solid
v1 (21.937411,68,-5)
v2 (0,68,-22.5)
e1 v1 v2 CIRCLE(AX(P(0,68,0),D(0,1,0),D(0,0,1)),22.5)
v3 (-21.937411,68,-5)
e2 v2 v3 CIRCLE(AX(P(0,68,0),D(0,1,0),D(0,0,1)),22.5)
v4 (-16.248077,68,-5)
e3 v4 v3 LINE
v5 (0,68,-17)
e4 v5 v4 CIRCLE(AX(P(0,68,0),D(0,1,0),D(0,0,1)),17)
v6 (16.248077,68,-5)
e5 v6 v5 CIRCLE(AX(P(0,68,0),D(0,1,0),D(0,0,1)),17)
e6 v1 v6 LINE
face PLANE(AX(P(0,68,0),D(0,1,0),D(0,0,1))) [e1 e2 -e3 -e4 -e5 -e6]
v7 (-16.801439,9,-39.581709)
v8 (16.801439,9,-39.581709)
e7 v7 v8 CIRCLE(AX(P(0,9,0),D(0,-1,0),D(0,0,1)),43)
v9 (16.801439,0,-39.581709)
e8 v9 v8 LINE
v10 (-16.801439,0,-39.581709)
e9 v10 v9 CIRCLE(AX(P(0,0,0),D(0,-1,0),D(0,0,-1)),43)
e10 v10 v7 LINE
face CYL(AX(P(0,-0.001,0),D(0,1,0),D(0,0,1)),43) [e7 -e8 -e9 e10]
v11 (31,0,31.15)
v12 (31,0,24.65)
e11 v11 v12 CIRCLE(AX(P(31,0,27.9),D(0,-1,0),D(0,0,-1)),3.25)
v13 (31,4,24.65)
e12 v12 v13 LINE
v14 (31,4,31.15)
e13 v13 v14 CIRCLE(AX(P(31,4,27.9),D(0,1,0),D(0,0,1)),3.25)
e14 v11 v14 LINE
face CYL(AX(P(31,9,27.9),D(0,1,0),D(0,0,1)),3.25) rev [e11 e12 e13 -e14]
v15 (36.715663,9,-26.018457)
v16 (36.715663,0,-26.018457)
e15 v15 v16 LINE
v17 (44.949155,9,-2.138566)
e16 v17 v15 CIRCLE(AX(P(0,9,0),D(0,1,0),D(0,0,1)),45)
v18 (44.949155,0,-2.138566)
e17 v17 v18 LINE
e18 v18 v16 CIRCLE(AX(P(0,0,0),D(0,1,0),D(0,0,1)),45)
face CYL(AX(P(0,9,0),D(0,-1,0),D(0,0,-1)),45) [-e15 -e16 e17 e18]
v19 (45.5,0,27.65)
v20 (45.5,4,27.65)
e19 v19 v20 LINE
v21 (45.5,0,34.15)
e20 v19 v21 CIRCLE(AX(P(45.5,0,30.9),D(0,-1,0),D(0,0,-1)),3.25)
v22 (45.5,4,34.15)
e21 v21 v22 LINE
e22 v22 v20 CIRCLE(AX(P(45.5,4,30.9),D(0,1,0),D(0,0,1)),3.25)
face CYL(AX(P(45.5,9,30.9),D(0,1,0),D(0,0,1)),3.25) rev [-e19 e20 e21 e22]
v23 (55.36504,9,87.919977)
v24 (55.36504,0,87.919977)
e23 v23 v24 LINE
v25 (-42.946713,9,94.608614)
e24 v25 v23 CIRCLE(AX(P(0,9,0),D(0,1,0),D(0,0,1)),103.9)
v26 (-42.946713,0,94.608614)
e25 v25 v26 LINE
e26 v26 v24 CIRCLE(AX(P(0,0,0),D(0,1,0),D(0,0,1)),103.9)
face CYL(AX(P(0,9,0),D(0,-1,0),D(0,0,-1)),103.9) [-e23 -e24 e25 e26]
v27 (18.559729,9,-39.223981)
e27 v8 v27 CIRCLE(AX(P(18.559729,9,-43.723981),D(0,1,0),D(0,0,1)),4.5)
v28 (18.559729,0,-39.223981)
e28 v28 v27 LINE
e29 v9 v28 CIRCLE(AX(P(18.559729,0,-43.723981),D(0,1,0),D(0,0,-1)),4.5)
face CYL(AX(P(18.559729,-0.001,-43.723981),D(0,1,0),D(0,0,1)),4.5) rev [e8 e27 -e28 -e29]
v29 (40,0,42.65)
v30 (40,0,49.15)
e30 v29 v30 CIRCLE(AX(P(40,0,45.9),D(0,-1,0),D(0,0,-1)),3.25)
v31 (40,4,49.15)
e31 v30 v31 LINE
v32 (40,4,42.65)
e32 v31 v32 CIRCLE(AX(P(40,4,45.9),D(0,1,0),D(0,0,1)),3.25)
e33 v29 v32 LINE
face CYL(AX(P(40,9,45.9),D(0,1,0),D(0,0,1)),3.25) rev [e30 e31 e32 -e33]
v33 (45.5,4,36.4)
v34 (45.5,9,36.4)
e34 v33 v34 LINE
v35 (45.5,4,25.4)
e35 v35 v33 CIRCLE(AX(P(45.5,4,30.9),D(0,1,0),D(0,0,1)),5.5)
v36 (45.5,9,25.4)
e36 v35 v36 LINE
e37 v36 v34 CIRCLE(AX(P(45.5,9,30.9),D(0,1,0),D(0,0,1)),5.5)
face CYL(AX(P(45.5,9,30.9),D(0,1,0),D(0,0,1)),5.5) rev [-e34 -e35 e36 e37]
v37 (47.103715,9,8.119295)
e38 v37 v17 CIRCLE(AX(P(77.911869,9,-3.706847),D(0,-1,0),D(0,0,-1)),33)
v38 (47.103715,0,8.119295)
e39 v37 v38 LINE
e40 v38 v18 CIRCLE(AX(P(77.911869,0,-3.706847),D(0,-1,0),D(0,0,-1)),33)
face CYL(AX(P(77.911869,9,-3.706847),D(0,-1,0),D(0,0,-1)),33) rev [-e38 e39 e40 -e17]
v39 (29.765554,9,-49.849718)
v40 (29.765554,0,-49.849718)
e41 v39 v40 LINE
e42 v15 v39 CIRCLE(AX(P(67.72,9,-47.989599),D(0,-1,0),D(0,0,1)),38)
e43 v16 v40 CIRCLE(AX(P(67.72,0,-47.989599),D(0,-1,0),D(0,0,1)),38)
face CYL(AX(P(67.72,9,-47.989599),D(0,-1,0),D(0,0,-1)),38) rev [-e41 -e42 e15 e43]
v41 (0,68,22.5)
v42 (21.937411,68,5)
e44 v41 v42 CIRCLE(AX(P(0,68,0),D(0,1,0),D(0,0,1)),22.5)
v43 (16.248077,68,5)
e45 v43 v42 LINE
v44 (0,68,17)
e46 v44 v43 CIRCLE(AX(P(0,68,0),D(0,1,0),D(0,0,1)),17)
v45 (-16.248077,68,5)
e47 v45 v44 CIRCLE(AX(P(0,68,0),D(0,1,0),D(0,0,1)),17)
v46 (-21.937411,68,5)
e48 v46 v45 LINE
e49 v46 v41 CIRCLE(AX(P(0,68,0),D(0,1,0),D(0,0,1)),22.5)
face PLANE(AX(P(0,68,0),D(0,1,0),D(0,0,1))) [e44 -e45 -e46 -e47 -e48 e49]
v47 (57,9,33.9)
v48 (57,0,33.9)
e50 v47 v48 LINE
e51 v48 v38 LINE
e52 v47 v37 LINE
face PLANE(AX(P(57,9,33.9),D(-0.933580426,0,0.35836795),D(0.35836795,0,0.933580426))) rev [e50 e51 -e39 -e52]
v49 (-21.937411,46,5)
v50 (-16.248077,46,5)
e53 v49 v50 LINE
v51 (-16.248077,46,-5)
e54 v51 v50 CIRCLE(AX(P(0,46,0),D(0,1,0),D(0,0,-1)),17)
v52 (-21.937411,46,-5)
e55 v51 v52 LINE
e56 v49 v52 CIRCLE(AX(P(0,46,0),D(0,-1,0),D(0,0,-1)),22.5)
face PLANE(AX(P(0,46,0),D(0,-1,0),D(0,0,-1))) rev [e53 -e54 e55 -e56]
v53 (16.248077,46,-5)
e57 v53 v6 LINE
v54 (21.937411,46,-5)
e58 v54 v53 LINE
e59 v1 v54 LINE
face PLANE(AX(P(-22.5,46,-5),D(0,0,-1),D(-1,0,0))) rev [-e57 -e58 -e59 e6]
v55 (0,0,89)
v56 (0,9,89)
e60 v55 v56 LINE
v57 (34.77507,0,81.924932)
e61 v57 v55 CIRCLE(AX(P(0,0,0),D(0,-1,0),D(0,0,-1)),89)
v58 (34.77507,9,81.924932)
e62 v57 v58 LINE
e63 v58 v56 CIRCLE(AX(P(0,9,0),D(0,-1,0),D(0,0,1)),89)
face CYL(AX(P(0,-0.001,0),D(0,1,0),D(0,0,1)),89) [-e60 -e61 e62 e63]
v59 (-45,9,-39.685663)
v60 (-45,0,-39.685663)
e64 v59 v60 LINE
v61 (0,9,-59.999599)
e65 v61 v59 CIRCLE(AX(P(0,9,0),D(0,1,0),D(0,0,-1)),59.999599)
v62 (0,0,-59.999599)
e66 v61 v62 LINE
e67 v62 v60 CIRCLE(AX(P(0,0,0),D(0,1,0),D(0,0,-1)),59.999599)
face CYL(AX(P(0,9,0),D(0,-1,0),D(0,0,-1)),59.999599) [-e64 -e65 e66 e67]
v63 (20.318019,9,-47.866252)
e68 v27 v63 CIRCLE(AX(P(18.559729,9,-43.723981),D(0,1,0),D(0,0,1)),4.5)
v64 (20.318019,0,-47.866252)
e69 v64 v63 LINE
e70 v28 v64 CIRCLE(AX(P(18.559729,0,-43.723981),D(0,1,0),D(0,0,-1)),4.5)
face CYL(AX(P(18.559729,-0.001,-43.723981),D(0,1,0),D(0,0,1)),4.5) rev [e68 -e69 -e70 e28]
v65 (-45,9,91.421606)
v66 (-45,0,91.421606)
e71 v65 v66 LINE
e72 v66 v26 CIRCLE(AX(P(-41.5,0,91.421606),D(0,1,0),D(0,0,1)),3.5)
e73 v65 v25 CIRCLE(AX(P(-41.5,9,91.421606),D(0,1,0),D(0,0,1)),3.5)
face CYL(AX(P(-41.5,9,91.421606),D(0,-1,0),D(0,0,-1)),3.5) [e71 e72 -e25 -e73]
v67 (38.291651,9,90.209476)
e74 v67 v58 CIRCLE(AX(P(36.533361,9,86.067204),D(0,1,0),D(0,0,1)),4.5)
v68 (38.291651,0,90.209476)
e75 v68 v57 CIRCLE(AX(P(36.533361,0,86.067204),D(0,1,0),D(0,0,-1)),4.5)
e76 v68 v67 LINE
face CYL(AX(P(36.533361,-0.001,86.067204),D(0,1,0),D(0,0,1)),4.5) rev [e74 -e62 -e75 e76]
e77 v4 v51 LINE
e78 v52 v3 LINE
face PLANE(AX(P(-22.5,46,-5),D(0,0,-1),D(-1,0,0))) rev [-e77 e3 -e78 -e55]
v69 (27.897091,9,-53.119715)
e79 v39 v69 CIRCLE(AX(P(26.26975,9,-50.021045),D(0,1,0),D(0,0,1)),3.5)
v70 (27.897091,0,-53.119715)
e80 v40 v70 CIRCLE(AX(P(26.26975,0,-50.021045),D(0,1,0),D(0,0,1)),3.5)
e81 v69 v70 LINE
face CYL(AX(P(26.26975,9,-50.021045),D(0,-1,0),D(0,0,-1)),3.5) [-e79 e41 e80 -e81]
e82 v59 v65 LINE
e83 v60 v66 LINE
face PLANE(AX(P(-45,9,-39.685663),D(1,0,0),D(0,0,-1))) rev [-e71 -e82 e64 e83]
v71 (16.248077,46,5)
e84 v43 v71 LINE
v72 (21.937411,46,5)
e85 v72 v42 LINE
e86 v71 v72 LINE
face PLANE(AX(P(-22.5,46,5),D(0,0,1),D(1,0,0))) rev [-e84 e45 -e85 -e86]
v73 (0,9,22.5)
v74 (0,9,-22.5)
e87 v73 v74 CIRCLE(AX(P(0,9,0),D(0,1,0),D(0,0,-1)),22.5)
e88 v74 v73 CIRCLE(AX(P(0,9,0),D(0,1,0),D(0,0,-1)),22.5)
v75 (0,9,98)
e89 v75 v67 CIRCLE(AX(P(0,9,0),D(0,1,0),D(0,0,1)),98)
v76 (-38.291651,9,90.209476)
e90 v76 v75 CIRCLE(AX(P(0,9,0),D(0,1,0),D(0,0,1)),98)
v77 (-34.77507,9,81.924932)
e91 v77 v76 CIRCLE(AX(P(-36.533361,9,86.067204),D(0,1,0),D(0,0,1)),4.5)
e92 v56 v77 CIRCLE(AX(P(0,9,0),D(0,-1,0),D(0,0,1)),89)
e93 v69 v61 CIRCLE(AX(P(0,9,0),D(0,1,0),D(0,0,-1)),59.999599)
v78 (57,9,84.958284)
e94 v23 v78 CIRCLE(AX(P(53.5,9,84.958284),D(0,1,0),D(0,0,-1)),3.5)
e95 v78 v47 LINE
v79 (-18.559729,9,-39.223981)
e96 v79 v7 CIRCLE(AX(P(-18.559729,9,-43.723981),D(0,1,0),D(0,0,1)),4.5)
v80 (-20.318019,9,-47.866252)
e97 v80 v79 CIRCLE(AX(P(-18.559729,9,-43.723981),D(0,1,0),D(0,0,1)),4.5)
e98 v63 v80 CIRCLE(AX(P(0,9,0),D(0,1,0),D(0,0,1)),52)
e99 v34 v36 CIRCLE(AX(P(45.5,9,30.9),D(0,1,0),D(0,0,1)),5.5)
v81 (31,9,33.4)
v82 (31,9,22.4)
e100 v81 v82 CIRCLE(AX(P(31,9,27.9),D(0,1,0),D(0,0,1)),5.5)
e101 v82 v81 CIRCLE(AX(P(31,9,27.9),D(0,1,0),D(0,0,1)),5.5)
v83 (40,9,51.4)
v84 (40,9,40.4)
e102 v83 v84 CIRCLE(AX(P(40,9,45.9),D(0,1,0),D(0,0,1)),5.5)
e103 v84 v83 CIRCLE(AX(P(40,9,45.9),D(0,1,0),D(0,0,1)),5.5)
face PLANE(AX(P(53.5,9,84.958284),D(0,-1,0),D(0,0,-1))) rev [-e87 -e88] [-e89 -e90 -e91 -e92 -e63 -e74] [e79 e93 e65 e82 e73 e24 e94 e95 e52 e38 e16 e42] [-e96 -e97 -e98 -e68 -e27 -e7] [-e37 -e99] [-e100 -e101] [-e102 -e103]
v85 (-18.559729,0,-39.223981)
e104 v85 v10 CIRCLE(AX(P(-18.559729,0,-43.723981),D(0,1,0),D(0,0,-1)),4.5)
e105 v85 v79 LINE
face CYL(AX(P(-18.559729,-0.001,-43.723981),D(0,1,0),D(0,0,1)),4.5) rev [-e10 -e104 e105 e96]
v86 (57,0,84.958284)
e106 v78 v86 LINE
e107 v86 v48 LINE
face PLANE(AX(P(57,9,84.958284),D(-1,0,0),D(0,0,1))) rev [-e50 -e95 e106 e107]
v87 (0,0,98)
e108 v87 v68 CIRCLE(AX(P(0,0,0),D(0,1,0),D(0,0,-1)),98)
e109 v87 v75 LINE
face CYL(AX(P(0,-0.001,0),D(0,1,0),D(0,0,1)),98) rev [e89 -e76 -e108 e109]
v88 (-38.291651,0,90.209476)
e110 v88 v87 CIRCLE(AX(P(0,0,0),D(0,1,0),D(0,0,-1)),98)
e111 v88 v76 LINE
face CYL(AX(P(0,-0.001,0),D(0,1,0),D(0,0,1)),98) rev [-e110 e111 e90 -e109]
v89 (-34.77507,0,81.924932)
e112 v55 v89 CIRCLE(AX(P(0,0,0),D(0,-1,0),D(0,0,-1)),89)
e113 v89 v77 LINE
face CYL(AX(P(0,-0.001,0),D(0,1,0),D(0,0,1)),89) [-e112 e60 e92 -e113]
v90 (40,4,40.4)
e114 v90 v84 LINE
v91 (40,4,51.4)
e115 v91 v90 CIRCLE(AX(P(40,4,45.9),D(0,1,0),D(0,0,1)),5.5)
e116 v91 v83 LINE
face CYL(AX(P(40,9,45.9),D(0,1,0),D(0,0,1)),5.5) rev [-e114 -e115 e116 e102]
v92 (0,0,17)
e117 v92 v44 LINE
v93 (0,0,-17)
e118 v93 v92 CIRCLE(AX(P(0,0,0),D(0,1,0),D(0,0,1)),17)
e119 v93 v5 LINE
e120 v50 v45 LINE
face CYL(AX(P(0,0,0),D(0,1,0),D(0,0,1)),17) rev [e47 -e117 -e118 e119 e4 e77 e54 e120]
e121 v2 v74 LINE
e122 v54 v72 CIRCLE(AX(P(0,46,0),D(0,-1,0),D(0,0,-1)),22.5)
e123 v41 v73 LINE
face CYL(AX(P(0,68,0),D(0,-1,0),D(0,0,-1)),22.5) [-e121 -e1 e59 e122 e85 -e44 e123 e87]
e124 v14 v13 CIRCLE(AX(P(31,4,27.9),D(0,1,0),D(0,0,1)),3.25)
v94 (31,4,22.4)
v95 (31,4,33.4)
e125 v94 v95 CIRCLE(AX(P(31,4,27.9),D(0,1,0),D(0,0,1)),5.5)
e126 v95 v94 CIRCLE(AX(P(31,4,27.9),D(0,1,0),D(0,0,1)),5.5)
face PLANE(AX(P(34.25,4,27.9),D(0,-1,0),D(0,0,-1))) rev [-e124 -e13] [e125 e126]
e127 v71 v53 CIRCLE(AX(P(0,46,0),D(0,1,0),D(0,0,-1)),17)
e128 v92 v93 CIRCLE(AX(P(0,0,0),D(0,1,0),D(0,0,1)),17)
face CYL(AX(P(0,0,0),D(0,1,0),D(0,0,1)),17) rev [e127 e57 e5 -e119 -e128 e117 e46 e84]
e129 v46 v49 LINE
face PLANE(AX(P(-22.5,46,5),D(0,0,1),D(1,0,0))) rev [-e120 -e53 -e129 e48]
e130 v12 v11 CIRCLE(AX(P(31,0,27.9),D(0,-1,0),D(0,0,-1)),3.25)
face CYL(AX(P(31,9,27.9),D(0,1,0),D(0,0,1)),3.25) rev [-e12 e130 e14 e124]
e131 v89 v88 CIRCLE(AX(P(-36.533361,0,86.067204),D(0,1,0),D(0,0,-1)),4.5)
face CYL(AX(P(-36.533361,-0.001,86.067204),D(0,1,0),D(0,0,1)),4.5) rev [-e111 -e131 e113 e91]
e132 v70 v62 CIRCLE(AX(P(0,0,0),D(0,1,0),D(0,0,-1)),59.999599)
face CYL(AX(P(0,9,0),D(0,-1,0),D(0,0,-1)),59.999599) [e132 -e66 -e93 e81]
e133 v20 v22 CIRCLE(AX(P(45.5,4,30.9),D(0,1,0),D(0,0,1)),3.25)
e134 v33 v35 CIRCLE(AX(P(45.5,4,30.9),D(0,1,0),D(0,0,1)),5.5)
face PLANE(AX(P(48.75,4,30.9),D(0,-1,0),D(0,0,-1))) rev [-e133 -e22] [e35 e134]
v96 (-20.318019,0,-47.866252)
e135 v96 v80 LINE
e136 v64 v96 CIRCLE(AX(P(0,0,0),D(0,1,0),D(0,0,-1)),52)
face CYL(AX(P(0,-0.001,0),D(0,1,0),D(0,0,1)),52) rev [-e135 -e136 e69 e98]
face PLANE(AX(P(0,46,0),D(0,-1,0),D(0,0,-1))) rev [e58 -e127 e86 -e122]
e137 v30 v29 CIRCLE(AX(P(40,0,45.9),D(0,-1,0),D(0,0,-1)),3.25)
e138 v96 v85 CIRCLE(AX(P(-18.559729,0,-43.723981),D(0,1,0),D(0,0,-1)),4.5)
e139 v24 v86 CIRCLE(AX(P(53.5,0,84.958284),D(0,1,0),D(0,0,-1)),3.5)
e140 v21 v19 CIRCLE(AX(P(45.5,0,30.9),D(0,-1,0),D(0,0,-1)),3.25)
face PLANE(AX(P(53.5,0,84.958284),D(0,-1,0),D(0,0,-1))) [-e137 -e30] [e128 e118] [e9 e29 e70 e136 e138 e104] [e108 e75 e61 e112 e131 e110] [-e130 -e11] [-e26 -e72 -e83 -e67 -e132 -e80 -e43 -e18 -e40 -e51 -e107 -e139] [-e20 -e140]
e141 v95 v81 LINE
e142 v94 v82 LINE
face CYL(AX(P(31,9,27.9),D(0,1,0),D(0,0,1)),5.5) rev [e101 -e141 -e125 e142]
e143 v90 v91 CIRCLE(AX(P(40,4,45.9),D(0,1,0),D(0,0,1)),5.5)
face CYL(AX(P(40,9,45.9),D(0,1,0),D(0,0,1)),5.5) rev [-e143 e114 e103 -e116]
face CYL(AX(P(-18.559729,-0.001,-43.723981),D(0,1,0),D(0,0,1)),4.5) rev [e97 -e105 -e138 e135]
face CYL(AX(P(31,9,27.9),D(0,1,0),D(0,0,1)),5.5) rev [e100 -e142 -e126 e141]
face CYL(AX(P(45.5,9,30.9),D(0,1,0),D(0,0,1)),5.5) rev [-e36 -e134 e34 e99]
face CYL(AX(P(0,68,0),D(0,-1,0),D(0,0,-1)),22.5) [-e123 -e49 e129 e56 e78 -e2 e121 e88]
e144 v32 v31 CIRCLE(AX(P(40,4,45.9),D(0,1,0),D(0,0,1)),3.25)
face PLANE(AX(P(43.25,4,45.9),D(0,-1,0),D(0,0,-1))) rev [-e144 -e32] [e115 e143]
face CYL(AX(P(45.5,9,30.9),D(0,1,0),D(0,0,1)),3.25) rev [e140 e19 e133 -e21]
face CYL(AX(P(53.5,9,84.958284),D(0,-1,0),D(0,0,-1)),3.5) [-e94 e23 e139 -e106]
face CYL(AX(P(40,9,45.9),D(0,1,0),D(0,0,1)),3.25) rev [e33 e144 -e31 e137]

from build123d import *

# Parameters (mm, degrees)
CAM_PLATE_9MM_DEPTH                = 9
ARC_SLOTS_REACH                    = 120.85
COUNTERBORED_HOLES_6_5_D           = 6.5
COUNTERBORED_HOLES_6_5_CBORE_D     = 11
COUNTERBORED_HOLES_6_5_CBORE_DEPTH = 5
HUB_PROFILE_45_R                   = 22.5
HUB_45_DEPTH                       = 59
HUB_BORE_PROFILE_34_R              = 17
HUB_BORE_34_DEPTH                  = 137.631658118
HUB_SLOTS_PROFILE_W                = 45
HUB_SLOTS_PROFILE_H                = 10
HUB_SLOTS_10MM_DEPTH               = 22


with BuildPart() as part:
    # Cam Plate Profile → Cam Plate 9mm (new body)
    with BuildSketch(Plane(origin=(0, 0, 0), x_dir=(1, 0, 0), z_dir=(0, 1, 0))):
        with BuildLine():
            Line((-45, 39.685663216), (-45, -91.421605761))
            ThreePointArc((-45, -91.421605761), (-44.442235206, -93.317193267), (-42.946713147, -94.60861393))
            ThreePointArc((-42.946713147, -94.60861393), (7.05252971, -103.660367666), (55.365039841, -87.919977044))
            ThreePointArc((55.365039841, -87.919977044), (56.564118098, -86.649786254), (57, -84.958283881))
            Line((57, -84.958283881), (57, -33.9))
            Line((57, -33.9), (47.103714625, -8.119295188))
            ThreePointArc((47.103714625, -8.119295188), (45.616562216, -3.076454346), (44.949155019, 2.138565661))
            ThreePointArc((44.949155019, 2.138565661), (42.542307371, 14.668063387), (36.715662651, 26.01845722))
            ThreePointArc((36.715662651, 26.01845722), (31.239721897, 37.350552414), (29.765554185, 49.849717914))
            ThreePointArc((29.765554185, 49.849717914), (29.308643796, 51.757455991), (27.897091162, 53.119715451))
            ThreePointArc((27.897091162, 53.119715451), (-10.874089044, 59.005983191), (-45, 39.685663216))
        make_face()
    extrude(amount=CAM_PLATE_9MM_DEPTH)

    # Arc Slots Profile → Arc Slots (cut, up to next)
    with BuildSketch(Plane(origin=(0, 9, 0), x_dir=(1, 0, 0), z_dir=(0, 1, 0)), mode=Mode.PRIVATE) as arc_slots_sk1:
        with BuildLine():
            ThreePointArc((20.318018681, 47.86625238), (0, 52), (-20.318018681, 47.86625238))
            ThreePointArc((-20.318018681, 47.86625238), (-22.702000444, 41.965690461), (-16.801438525, 39.581708698))
            ThreePointArc((-16.801438525, 39.581708698), (0, 43), (16.801438525, 39.581708698))
            ThreePointArc((16.801438525, 39.581708698), (22.702000444, 41.965690461), (20.318018681, 47.86625238))
        make_face()
    arc_slots_tool1 = extrude(arc_slots_sk1.sketch, amount=-ARC_SLOTS_REACH, mode=Mode.PRIVATE) & part.part
    # Arc Slots Profile → Arc Slots (cut, up to next)
    with BuildSketch(Plane(origin=(0, 9, 0), x_dir=(1, 0, 0), z_dir=(0, 1, 0)), mode=Mode.PRIVATE) as arc_slots_sk2:
        with BuildLine():
            ThreePointArc((-38.291650592, -90.209475638), (0, -98), (38.291650592, -90.209475638))
            ThreePointArc((38.291650592, -90.209475638), (40.675632354, -84.30891372), (34.775070436, -81.924931957))
            ThreePointArc((34.775070436, -81.924931957), (0, -89), (-34.775070436, -81.924931957))
            ThreePointArc((-34.775070436, -81.924931957), (-40.675632354, -84.30891372), (-38.291650592, -90.209475638))
        make_face()
    arc_slots_tool2 = extrude(arc_slots_sk2.sketch, amount=-ARC_SLOTS_REACH, mode=Mode.PRIVATE) & part.part
    add(arc_slots_tool1.solids().sort_by_distance((0, 9, -45.841951))[0], mode=Mode.SUBTRACT)
    add(arc_slots_tool2.solids().sort_by_distance((0, 9, 90.583722))[0], mode=Mode.SUBTRACT)

    # Counterbored Holes Ø6.5 (through all)
    with Locations(Plane(origin=(31, 9, 27.9), x_dir=(0, 0, 1), z_dir=(0, 1, 0))):
        with Locations((0, 0), (3, 14.5), (18, 9)):
            CounterBoreHole(COUNTERBORED_HOLES_6_5_D / 2, COUNTERBORED_HOLES_6_5_CBORE_D / 2, COUNTERBORED_HOLES_6_5_CBORE_DEPTH)

    # Hub Profile Ø45 → Hub Ø45 (add)
    with BuildSketch(Plane(origin=(0, 9, 0), x_dir=(1, 0, 0), z_dir=(0, 1, 0))):
        with Locations(Location((0, 0, 0), (0, 0, 90))):
            Circle(HUB_PROFILE_45_R)
    extrude(amount=HUB_45_DEPTH)

    # Hub Bore Profile Ø34 → Hub Bore Ø34 (cut, through all)
    with BuildSketch(Plane(origin=(0, 68, 0), x_dir=(1, 0, 0), z_dir=(0, 1, 0))):
        with Locations(Location((0, 0, 0), (0, 0, 270))):
            Circle(HUB_BORE_PROFILE_34_R)
    extrude(amount=-HUB_BORE_34_DEPTH, mode=Mode.SUBTRACT)

    # Hub Slots Profile → Hub Slots 10mm (cut)
    with BuildSketch(Plane(origin=(0, 68, 0), x_dir=(1, 0, 0), z_dir=(0, 1, 0))):
        Rectangle(HUB_SLOTS_PROFILE_W, HUB_SLOTS_PROFILE_H)
    extrude(amount=-HUB_SLOTS_10MM_DEPTH, mode=Mode.SUBTRACT)


solid = part.part
